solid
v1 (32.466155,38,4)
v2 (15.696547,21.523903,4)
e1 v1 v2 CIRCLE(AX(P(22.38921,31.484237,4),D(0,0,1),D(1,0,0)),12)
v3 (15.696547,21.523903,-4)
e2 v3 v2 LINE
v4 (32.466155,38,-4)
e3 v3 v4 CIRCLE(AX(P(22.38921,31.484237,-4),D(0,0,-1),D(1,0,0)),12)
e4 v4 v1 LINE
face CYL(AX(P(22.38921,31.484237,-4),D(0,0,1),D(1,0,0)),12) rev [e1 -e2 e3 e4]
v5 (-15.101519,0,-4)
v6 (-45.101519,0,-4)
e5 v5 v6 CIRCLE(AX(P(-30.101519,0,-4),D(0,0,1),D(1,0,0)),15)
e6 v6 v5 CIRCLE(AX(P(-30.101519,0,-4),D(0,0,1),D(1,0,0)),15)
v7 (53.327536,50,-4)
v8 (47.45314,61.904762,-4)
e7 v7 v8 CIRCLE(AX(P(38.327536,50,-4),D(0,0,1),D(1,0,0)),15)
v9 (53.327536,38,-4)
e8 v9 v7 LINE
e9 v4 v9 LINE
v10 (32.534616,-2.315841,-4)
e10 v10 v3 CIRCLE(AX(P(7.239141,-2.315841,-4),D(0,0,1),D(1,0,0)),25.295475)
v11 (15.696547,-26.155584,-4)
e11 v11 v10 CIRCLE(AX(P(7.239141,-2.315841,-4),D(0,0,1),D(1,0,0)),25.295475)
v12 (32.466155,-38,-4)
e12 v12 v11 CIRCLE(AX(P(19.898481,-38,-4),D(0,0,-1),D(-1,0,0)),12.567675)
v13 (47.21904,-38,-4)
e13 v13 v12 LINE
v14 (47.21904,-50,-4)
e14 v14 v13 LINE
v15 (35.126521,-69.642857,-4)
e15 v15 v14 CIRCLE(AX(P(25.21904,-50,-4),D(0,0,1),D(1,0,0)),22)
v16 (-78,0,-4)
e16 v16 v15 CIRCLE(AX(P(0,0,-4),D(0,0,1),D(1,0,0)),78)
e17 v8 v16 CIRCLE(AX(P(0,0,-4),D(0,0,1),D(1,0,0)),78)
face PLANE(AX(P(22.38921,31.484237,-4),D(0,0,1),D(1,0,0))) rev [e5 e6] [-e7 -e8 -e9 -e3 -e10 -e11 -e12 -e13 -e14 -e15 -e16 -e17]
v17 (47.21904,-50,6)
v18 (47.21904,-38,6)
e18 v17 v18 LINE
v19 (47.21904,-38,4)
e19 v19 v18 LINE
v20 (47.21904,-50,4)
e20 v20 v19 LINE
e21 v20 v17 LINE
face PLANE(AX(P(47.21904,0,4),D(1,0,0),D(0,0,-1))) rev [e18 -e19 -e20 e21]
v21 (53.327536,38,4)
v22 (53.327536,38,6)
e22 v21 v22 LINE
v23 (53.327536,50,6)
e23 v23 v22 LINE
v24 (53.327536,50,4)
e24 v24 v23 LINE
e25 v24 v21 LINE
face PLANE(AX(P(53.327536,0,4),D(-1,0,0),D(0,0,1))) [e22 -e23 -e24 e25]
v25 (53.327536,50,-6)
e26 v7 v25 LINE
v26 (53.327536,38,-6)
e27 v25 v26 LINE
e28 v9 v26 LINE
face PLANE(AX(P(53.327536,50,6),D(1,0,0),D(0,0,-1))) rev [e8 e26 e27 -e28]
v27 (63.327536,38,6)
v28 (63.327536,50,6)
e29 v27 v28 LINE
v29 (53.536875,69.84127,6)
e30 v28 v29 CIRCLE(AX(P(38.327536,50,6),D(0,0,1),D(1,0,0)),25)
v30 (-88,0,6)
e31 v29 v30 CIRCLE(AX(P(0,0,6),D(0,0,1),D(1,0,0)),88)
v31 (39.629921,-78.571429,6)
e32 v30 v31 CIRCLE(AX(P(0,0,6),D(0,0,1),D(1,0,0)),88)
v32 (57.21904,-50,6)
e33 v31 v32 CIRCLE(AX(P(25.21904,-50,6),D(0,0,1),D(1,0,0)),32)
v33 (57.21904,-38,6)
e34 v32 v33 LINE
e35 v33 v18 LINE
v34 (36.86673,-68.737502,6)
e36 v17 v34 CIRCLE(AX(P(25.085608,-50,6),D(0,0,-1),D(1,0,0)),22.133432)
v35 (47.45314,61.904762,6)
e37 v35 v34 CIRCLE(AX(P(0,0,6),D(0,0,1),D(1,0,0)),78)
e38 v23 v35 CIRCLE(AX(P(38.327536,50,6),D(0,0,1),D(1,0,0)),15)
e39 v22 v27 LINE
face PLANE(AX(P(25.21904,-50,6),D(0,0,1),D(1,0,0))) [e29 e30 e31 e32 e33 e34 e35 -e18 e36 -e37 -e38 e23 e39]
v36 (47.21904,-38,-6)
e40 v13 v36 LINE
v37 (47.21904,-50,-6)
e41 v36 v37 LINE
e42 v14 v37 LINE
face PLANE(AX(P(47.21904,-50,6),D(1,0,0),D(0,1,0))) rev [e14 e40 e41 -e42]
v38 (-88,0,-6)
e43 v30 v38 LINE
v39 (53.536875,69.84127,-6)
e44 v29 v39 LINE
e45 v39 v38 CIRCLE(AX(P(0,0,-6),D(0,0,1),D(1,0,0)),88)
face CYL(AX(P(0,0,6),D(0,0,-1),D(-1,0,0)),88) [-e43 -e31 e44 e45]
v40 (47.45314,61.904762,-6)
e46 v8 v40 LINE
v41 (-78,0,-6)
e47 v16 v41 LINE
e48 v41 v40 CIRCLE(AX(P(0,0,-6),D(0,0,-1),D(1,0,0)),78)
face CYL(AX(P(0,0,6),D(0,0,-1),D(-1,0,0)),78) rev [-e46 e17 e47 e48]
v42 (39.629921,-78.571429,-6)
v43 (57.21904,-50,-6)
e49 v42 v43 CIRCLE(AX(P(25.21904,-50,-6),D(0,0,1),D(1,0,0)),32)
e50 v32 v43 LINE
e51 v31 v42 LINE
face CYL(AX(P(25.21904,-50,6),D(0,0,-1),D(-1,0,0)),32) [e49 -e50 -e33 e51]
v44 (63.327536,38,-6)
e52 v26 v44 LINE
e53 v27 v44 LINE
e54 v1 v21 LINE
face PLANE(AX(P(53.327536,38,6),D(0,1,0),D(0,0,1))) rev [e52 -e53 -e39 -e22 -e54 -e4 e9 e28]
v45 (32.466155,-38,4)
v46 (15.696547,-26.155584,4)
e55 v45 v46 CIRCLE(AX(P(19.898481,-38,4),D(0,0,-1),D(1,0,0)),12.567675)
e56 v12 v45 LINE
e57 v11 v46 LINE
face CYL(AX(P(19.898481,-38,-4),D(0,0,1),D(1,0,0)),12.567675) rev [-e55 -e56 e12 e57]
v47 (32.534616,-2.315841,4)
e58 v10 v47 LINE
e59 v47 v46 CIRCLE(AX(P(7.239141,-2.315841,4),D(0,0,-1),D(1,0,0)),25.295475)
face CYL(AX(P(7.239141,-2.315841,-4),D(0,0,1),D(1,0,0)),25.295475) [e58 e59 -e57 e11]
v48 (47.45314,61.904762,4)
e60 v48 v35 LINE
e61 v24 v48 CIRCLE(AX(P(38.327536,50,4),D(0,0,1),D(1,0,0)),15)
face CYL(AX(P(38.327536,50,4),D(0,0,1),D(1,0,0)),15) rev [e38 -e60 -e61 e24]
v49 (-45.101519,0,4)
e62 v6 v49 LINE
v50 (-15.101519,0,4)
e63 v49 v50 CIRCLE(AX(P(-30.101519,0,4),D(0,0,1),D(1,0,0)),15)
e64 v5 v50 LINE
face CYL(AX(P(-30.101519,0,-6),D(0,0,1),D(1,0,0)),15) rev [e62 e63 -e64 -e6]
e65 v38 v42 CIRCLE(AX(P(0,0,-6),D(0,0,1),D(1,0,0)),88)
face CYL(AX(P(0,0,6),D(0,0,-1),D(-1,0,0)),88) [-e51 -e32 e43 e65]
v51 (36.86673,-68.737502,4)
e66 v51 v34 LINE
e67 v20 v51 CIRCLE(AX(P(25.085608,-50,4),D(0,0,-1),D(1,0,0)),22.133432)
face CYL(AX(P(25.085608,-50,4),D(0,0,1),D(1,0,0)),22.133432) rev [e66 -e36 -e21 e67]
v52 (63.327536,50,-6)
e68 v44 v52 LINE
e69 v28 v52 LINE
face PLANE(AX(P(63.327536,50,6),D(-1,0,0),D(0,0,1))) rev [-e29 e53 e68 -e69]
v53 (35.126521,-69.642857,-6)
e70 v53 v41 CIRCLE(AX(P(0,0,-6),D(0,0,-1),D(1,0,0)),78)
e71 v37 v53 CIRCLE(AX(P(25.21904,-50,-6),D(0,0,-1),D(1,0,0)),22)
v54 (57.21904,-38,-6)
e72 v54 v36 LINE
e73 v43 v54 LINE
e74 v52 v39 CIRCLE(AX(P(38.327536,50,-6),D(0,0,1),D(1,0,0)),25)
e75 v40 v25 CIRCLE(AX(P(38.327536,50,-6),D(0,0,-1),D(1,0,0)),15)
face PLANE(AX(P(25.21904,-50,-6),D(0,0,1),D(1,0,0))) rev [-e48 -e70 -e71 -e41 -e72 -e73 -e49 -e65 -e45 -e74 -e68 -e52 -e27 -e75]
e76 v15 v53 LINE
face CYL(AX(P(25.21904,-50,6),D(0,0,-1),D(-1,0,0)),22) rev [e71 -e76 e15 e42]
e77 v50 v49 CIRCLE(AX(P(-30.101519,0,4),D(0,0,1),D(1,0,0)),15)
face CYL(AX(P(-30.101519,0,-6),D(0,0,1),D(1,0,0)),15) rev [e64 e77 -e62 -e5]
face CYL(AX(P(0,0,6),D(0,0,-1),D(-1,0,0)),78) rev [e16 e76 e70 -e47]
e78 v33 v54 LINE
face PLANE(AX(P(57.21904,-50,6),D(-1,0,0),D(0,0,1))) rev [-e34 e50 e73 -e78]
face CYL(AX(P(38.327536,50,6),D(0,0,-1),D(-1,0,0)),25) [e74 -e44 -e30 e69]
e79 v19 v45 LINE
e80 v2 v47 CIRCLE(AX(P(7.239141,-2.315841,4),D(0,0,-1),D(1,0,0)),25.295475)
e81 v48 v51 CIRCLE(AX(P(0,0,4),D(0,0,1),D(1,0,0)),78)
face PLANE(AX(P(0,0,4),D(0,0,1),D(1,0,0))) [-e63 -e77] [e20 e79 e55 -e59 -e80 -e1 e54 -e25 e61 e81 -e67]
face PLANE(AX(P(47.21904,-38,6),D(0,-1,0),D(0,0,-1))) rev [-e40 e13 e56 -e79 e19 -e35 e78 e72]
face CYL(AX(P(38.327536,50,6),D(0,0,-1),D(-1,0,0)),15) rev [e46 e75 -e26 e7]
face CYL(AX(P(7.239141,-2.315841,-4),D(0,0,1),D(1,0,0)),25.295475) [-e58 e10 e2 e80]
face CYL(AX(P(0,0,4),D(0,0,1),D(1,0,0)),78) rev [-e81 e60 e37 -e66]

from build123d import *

# Parameters (mm, degrees)
FRAME_PLATE_12MM_DEPTH      = 6
RIM_BOSS_DEPTH              = 10
FACE_RECESS_2MM_DEPTH       = 2
UPPER_START                 = 2
UPPER_RELIEF_CUT_SKETCH_R   = 25
UPPER_RELIEF_CUT_2MM_DEPTH  = 2
CENTRE_RELIEF_CUT_2MM_DEPTH = 2
LOWER_RELIEF_CUT_SKETCH_R   = 52.651518039
LOWER_RELIEF_CUT_2MM_DEPTH  = 2
JAW_OPENING_SKETCH_R        = 15
JAW_OPENING_CUT_DEPTH       = 125.85191228


with BuildPart() as part:
    # Frame Profile Sketch → Frame Plate 12mm (new, symmetric)
    with BuildSketch(Plane.XY):
        with BuildLine():
            Line((57.219040426, -50), (57.219040426, -38))
            Line((57.219040426, -38), (47.219040426, -38))
            Line((47.219040426, -38), (47.219040426, -50))
            ThreePointArc((47.219040426, -50), (43.953561552, -61.533330749), (35.126520593, -69.642857143))
            ThreePointArc((35.126520593, -69.642857143), (-77.659797107, 7.277081367), (47.453139554, 61.904761905))
            ThreePointArc((47.453139554, 61.904761905), (51.779005163, 56.637617931), (53.327535793, 50))
            Line((53.327535793, 50), (53.327535793, 38))
            Line((53.327535793, 38), (63.327535793, 38))
            Line((63.327535793, 38), (63.327535793, 50))
            ThreePointArc((63.327535793, 50), (60.74665141, 61.062696552), (53.536875394, 69.841269841))
            ThreePointArc((53.536875394, 69.841269841), (-87.616181352, 8.210040517), (39.629920669, -78.571428571))
            ThreePointArc((39.629920669, -78.571428571), (52.469252974, -66.775753816), (57.219040426, -50))
        make_face()
    extrude(amount=FRAME_PLATE_12MM_DEPTH, both=True)

    # Rim Boss Sketch → Rim Boss (add)
    with BuildSketch(Plane.XY.offset(6)):
        with BuildLine():
            Line((53.327535793, 38), (32.46615526, 38))
            ThreePointArc((32.46615526, 38), (13.979168764, 40.044097465), (15.696546582, 21.523902608))
            ThreePointArc((15.696546582, 21.523902608), (32.534616457, -2.315840538), (15.696546582, -26.155583684))
            ThreePointArc((15.696546582, -26.155583684), (12.648035491, -48.265354025), (32.46615526, -38))
            Line((32.46615526, -38), (47.219040426, -38))
            Line((47.219040426, -38), (47.219040426, -50))
            ThreePointArc((47.219040426, -50), (43.953561552, -61.533330749), (35.126520593, -69.642857143))
            ThreePointArc((35.126520593, -69.642857143), (-77.659797107, 7.277081367), (47.453139554, 61.904761905))
            ThreePointArc((47.453139554, 61.904761905), (51.779005163, 56.637617931), (53.327535793, 50))
            Line((53.327535793, 50), (53.327535793, 38))
        make_face()
    extrude(amount=-RIM_BOSS_DEPTH)

    # Face Recess Sketch → Face Recess 2mm (cut)
    with BuildSketch(Plane.XY.offset(6)):
        with BuildLine():
            ThreePointArc((36.866729899, -68.73750233), (44.45885626, -60.703554629), (47.219040426, -50))
            Line((47.219040426, -50), (47.219040426, -38))
            Line((47.219040426, -38), (32.46615526, -38))
            ThreePointArc((32.46615526, -38), (30.153940112, -45.264433679), (24.06810264, -49.855829743))
            ThreePointArc((24.06810264, -49.855829743), (7.879587743, -42.091412935), (15.644004551, -25.902898038))
            ThreePointArc((15.644004551, -25.902898038), (32.325529371, -3.417209672), (17.682148152, 20.445959399))
            ThreePointArc((17.682148152, 20.445959399), (16.663921846, 20.938096482), (15.696546582, 21.523902608))
            ThreePointArc((15.696546582, 21.523902608), (13.979168764, 40.044097465), (32.46615526, 38))
            Line((32.46615526, 38), (53.327535793, 38))
            Line((53.327535793, 38), (53.327535793, 50))
            ThreePointArc((53.327535793, 50), (51.779005163, 56.637617931), (47.453139554, 61.904761905))
            ThreePointArc((47.453139554, 61.904761905), (-77.745163176, 6.299968474), (36.866729899, -68.73750233))
        make_face()
    extrude(amount=-FACE_RECESS_2MM_DEPTH, mode=Mode.SUBTRACT)

    # Upper Relief Cut Sketch → Upper Relief Cut 2mm (cut)
    with BuildSketch(Plane.XY.offset(4).offset(UPPER_START)):
        with Locations((7.349665755, -2.318921614)):
            Circle(UPPER_RELIEF_CUT_SKETCH_R)
    extrude(amount=-UPPER_RELIEF_CUT_2MM_DEPTH, mode=Mode.SUBTRACT)

    # Centre Relief Cut Sketch → Centre Relief Cut 2mm (cut)
    with BuildSketch(Plane.XY.offset(4)):
        with BuildLine():
            ThreePointArc((23.833190109, -22.398989717), (-15.184880461, 28.968173855), (4.862308851, -32.34337094))
            ThreePointArc((4.862308851, -32.34337094), (27.276572021, -52.035475846), (23.833190109, -22.398989717))
        make_face()
    extrude(amount=CENTRE_RELIEF_CUT_2MM_DEPTH, mode=Mode.SUBTRACT)

    # Lower Relief Cut Sketch → Lower Relief Cut 2mm (cut)
    with BuildSketch(Plane.XY.offset(4)):
        with Locations((-7.330378767, 0)):
            Circle(LOWER_RELIEF_CUT_SKETCH_R)
    extrude(amount=LOWER_RELIEF_CUT_2MM_DEPTH, mode=Mode.SUBTRACT)

    # Jaw Opening Sketch → Jaw Opening Cut (cut, through all)
    with BuildSketch(Plane.XY.offset(4)):
        with Locations((-30.10151943, 0)):
            Circle(JAW_OPENING_SKETCH_R)
    extrude(amount=-JAW_OPENING_CUT_DEPTH, mode=Mode.SUBTRACT)


solid = part.part
